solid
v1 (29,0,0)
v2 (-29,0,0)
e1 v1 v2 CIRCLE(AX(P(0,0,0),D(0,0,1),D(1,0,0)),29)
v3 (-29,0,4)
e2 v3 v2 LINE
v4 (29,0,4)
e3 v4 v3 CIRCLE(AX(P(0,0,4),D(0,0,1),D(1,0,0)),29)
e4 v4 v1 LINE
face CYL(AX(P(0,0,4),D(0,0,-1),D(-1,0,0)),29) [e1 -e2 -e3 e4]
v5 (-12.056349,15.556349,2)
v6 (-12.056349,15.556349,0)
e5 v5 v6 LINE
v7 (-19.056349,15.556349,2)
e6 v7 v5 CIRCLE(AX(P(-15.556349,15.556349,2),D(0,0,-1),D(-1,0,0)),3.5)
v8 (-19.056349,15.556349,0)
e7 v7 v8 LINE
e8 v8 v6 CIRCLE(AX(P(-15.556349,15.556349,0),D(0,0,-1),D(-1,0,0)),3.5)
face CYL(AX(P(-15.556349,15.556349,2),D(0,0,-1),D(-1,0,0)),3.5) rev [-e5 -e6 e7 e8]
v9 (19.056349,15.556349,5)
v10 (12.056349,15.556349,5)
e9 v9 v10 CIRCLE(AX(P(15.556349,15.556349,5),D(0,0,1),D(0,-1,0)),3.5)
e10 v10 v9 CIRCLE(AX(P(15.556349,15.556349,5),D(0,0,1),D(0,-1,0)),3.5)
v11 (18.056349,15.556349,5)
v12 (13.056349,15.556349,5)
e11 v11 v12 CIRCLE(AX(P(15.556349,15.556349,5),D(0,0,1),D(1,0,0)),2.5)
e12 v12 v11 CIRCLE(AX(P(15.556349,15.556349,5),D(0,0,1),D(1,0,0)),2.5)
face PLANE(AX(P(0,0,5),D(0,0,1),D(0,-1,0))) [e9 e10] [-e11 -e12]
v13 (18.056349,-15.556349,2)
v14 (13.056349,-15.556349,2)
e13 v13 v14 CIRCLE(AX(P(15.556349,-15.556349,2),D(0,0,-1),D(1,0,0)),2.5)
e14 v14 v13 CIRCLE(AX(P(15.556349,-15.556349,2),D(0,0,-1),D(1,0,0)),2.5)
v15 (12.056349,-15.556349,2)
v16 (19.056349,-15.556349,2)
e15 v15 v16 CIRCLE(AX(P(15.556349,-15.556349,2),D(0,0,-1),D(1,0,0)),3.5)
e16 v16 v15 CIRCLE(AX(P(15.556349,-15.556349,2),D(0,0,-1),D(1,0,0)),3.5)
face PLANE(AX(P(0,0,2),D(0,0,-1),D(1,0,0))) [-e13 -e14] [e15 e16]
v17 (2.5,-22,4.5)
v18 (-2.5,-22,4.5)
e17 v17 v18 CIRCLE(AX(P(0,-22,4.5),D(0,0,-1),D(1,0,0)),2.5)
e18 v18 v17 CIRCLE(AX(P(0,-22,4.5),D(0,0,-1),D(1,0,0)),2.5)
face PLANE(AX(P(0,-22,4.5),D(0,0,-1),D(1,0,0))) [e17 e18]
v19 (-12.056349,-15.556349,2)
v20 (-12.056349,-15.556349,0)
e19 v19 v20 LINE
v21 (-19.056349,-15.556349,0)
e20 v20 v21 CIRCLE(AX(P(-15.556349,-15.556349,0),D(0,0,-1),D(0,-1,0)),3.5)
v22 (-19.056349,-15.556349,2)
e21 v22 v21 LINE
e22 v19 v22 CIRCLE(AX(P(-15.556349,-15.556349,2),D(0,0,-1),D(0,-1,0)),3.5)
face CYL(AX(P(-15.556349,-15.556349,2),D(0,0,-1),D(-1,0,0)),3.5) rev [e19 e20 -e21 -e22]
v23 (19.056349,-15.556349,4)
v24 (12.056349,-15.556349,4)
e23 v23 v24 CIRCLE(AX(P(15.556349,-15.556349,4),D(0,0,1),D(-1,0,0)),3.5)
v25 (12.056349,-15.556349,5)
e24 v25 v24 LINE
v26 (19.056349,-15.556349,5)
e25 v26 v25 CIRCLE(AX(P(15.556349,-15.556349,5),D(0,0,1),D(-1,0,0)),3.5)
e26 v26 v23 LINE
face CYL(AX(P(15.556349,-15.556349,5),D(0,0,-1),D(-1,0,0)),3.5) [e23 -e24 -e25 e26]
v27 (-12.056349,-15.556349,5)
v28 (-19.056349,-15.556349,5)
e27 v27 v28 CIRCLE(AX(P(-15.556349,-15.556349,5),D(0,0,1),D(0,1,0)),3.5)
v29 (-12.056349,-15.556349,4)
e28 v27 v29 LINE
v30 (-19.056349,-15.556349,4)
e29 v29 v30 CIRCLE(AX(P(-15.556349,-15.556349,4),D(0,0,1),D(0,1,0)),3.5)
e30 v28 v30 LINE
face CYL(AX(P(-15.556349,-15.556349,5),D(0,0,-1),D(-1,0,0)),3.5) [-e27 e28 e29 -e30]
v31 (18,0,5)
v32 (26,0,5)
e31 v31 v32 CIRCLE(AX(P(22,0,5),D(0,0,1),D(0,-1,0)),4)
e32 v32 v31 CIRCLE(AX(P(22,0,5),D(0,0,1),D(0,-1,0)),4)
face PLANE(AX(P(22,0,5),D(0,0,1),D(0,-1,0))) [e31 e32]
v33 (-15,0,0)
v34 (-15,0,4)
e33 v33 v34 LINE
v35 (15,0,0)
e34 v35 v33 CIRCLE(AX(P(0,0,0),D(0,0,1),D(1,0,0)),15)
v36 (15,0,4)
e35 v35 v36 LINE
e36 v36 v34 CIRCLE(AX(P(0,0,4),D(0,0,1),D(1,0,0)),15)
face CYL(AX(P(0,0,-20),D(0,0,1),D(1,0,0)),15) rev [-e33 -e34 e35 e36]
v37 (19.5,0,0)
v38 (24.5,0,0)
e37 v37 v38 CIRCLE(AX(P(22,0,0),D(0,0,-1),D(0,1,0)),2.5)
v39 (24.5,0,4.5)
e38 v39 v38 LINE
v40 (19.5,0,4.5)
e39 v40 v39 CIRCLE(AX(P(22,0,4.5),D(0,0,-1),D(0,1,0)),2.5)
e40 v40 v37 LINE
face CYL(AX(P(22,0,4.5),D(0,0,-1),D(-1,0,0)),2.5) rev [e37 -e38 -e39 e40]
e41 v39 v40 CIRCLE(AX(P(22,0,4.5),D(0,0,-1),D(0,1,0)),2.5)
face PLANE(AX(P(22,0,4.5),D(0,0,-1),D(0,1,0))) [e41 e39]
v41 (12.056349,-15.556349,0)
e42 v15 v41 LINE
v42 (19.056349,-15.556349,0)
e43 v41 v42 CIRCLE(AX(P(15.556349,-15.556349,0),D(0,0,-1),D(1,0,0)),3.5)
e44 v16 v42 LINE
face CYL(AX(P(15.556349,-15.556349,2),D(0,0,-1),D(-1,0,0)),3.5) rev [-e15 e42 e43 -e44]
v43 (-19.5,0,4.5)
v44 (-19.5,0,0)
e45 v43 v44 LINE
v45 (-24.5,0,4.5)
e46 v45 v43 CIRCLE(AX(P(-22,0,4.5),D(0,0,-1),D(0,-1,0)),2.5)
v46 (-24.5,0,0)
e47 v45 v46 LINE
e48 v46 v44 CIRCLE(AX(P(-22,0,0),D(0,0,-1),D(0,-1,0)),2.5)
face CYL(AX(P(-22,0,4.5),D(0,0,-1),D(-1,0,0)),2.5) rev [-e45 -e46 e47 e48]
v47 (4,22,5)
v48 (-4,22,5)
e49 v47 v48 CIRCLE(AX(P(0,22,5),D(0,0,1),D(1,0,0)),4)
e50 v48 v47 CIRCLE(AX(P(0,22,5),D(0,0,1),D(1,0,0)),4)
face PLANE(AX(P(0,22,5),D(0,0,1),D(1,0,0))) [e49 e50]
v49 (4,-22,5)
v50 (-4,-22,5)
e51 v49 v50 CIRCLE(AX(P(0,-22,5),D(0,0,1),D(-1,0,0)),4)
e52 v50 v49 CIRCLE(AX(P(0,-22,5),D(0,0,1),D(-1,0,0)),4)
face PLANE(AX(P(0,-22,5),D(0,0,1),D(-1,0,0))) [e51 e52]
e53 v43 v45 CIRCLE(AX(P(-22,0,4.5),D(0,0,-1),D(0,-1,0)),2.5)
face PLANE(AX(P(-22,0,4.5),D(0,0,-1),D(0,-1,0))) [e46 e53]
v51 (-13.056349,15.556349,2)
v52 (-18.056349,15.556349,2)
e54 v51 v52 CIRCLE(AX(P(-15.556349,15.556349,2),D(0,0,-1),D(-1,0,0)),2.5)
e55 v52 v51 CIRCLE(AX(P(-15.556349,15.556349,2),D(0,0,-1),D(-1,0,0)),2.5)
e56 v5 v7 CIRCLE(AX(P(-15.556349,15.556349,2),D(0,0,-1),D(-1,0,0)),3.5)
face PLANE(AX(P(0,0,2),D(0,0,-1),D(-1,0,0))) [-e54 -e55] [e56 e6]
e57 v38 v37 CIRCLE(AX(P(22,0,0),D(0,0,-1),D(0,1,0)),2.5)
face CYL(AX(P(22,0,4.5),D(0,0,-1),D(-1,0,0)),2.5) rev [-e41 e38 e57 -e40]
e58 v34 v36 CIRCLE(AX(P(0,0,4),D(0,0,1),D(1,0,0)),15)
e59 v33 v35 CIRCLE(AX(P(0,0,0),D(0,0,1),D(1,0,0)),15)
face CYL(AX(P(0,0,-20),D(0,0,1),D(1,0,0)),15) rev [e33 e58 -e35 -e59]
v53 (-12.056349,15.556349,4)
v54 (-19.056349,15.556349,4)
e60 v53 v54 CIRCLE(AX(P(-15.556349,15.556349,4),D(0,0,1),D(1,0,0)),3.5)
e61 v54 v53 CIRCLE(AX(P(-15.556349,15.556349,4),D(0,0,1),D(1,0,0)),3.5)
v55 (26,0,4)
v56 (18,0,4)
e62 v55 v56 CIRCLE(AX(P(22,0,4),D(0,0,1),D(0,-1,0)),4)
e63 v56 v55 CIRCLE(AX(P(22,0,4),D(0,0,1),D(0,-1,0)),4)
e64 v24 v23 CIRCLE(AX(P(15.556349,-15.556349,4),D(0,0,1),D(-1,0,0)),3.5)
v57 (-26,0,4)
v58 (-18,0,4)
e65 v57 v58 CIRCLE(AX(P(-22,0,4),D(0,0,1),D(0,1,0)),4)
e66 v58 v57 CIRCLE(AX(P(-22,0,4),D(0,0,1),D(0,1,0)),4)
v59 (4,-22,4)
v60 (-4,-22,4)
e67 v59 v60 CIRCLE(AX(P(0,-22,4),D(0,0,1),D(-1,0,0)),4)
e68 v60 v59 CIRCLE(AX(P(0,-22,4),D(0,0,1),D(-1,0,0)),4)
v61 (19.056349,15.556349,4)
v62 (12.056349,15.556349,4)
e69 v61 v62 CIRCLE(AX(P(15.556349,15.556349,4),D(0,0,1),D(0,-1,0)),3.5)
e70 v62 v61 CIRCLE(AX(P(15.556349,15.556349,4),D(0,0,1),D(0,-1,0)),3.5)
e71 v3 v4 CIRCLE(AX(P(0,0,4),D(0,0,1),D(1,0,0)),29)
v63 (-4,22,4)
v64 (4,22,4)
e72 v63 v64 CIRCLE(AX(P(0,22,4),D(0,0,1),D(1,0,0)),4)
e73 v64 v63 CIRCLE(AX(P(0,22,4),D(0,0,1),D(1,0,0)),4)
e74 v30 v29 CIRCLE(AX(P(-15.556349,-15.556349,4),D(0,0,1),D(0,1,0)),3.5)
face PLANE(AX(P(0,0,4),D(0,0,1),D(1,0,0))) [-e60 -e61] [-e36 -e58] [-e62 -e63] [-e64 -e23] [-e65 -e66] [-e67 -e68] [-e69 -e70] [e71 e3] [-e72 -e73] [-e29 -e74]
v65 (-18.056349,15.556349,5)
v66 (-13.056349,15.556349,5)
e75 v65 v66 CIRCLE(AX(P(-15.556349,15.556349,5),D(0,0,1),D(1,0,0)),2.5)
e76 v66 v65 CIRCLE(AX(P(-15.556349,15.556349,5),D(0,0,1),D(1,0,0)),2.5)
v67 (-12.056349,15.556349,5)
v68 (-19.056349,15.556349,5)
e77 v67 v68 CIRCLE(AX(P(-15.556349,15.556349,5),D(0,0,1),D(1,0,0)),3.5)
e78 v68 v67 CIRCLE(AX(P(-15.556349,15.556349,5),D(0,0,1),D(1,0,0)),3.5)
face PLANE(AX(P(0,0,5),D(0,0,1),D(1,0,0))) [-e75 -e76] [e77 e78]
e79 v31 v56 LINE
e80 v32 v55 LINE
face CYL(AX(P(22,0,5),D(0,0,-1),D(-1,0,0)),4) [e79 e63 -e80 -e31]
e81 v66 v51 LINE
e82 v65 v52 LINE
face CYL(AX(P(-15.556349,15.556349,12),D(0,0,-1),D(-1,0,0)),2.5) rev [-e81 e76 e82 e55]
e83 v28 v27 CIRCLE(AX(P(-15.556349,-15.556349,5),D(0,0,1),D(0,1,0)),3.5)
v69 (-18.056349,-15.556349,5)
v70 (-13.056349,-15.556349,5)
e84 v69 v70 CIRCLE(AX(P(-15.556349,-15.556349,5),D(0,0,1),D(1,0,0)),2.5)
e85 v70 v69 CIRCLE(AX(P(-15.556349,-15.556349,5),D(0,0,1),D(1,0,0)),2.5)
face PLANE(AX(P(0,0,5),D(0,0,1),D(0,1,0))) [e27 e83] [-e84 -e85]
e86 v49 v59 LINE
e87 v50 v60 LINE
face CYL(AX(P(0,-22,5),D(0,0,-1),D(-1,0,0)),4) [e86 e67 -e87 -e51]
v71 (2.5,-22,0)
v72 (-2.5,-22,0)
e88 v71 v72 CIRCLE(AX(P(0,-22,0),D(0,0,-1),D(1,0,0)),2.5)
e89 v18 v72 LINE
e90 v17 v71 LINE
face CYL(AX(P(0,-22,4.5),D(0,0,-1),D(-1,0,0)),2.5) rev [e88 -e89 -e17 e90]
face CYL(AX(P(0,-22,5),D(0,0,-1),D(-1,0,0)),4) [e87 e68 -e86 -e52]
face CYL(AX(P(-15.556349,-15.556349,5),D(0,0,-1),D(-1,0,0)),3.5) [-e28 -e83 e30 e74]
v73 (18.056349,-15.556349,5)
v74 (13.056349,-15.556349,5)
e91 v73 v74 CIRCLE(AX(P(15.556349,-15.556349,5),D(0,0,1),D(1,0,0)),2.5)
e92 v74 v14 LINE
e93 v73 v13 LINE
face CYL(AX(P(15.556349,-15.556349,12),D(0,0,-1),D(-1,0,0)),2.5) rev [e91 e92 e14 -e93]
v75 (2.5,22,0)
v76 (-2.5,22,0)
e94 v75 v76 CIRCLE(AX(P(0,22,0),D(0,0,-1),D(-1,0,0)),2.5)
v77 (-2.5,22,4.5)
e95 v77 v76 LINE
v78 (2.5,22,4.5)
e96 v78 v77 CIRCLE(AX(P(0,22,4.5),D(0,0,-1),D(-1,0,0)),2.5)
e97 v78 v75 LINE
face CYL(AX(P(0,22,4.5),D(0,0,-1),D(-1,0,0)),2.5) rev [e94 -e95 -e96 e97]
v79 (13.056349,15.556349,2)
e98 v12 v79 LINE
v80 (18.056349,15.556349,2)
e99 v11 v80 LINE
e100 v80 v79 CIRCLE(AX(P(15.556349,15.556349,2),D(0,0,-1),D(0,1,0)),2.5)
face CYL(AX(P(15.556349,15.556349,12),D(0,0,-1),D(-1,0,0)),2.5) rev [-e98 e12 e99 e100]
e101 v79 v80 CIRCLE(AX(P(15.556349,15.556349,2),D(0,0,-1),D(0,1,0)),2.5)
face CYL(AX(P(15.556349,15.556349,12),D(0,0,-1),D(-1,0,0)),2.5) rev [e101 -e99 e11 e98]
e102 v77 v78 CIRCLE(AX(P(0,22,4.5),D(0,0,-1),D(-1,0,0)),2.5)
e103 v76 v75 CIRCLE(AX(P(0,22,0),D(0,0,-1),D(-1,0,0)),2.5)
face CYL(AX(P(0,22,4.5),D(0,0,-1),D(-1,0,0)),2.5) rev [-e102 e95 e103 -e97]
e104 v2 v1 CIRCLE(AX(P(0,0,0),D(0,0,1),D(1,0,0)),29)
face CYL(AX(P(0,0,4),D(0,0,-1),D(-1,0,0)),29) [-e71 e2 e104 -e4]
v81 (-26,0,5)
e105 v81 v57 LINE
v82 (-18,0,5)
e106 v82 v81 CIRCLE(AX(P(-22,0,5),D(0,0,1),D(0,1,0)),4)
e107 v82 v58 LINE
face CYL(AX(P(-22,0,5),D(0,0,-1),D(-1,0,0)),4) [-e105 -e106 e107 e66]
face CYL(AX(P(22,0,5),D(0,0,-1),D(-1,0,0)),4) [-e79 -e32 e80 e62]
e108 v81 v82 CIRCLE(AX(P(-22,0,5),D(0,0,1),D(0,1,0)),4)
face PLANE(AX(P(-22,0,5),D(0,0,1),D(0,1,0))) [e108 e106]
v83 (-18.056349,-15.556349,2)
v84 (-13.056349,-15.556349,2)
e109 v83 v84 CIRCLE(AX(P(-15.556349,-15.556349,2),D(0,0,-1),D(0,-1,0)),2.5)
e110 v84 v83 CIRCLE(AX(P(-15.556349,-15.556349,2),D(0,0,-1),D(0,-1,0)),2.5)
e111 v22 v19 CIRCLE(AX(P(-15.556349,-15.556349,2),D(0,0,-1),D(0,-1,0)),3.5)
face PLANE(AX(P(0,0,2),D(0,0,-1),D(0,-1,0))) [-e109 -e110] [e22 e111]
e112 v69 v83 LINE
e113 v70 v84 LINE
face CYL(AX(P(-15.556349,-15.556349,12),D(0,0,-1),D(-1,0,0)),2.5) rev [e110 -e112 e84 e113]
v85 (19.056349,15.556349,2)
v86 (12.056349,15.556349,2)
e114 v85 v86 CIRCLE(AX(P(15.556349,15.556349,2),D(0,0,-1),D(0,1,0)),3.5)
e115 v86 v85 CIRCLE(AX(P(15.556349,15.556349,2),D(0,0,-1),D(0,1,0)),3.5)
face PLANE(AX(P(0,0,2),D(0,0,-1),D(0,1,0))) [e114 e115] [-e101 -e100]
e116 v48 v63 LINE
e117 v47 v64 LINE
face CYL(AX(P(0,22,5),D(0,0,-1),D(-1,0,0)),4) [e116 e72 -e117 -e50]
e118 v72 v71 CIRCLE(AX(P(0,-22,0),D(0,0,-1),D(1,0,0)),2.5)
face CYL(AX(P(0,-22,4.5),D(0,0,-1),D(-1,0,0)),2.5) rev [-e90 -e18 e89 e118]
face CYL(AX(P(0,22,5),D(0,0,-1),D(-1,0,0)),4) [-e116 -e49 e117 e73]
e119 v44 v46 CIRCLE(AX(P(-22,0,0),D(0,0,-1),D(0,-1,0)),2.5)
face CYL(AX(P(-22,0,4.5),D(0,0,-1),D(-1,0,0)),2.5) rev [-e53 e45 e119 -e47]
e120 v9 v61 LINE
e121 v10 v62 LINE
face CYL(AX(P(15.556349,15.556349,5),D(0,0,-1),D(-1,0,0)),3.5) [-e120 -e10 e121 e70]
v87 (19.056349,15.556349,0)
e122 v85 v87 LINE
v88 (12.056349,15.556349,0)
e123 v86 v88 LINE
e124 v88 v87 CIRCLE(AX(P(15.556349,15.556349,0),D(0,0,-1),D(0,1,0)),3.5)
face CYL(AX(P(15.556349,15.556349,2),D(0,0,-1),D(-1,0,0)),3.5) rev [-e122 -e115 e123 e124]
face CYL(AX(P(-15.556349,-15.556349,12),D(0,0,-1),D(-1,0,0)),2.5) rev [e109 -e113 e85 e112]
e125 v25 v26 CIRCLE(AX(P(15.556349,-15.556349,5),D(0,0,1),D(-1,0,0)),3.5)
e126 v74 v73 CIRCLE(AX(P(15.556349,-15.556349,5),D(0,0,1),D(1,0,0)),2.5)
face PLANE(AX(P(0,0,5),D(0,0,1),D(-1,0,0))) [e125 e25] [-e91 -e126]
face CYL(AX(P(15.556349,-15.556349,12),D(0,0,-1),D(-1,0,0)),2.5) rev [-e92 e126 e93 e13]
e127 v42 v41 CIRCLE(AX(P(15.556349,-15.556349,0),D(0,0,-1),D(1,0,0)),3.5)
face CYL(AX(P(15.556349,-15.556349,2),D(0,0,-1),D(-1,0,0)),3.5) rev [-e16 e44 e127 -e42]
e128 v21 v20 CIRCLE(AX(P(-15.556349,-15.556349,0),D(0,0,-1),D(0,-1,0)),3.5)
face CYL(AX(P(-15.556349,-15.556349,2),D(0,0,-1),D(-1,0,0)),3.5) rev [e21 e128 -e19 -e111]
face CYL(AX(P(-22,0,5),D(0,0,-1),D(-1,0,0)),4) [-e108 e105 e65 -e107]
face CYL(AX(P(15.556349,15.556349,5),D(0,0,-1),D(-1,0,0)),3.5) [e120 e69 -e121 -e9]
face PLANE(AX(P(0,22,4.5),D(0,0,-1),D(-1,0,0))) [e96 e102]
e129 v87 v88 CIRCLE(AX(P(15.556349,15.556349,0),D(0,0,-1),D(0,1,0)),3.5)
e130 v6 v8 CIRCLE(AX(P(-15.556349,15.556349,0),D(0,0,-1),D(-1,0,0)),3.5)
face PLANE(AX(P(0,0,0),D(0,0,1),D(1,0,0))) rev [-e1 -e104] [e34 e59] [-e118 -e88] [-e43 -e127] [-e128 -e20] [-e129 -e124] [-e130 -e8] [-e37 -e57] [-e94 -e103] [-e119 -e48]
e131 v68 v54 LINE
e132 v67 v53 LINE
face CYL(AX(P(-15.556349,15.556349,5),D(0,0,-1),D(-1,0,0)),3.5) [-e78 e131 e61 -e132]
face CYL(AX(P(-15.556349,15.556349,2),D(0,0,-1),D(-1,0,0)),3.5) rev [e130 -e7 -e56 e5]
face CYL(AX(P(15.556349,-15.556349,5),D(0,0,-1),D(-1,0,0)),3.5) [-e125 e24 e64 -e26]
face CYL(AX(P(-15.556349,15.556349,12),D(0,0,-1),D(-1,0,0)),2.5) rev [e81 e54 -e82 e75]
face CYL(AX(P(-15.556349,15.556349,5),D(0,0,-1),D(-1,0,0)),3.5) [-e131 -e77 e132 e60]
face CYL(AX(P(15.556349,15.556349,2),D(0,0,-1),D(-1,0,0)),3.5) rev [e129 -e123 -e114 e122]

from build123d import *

# Parameters (mm, degrees)
SKETCH1_R           = 29
BOSS_EXTRUDE1_DEPTH = 4
SKETCH2_R           = 15
CUT_EXTRUDE1_DEPTH  = 24
SKETCH3_R           = 4
BOSS_EXTRUDE2_DEPTH = 1
SKETCH5_R           = 2.5
CUT_EXTRUDE2_DEPTH  = 4.5
CIRPATTERN1_COUNT   = 4
SKETCH6_R           = 3.5
BOSS_EXTRUDE3_DEPTH = 1
SKETCH7_R           = 3.5
CUT_EXTRUDE3_DEPTH  = 2
SKETCH8_R           = 2.5
CUT_EXTRUDE4_DEPTH  = 10
CIRPATTERN2_COUNT   = 4


with BuildPart() as part:
    # Sketch1 → Boss-Extrude1 (new body)
    with BuildSketch(Plane.XY):
        Circle(SKETCH1_R)
    extrude(amount=BOSS_EXTRUDE1_DEPTH)

    # Sketch2 → Cut-Extrude1 (cut)
    with BuildSketch(Plane.XY.offset(4)):
        Circle(SKETCH2_R)
    extrude(amount=-CUT_EXTRUDE1_DEPTH, mode=Mode.SUBTRACT)

    # Sketch3 → Boss-Extrude2 (add)
    with BuildSketch(Plane.XY.offset(4)):
        with Locations((0, 22)):
            Circle(SKETCH3_R)
    boss_extrude2 = extrude(amount=BOSS_EXTRUDE2_DEPTH)

    # Sketch5 → Cut-Extrude2 (cut)
    with BuildSketch(Plane(origin=(0, 0, 0), x_dir=(-1, 0, 0), z_dir=(0, 0, -1))):
        with Locations((0, 22)):
            Circle(SKETCH5_R)
    cut_extrude2 = extrude(amount=-CUT_EXTRUDE2_DEPTH, mode=Mode.SUBTRACT)

    # CirPattern1: Boss-Extrude2, Cut-Extrude2 ×4 about axis
    cirpattern1_axis = Axis((0, 0, 0), (0, 0, 1))
    add([boss_extrude2.rotate(cirpattern1_axis, i * 360 / CIRPATTERN1_COUNT) for i in range(1, CIRPATTERN1_COUNT)])
    add([cut_extrude2.rotate(cirpattern1_axis, i * 360 / CIRPATTERN1_COUNT) for i in range(1, CIRPATTERN1_COUNT)], mode=Mode.SUBTRACT)

    # Sketch6 → Boss-Extrude3 (add)
    with BuildSketch(Plane.XY.offset(4)):
        with Locations((-15.556349186, 15.556349186)):
            Circle(SKETCH6_R)
    boss_extrude3 = extrude(amount=BOSS_EXTRUDE3_DEPTH)

    # Sketch7 → Cut-Extrude3 (cut)
    with BuildSketch(Plane(origin=(0, 0, 0), x_dir=(-1, 0, 0), z_dir=(0, 0, -1))):
        with Locations(Location((15.556349186, 15.556349186, 0), (0, 0, 180))):
            Circle(SKETCH7_R)
    cut_extrude3 = extrude(amount=-CUT_EXTRUDE3_DEPTH, mode=Mode.SUBTRACT)

    # Sketch8 → Cut-Extrude4 (cut)
    with BuildSketch(Plane(origin=(0, 0, 2), x_dir=(-1, 0, 0), z_dir=(0, 0, -1))):
        with Locations((15.556349186, 15.556349186)):
            Circle(SKETCH8_R)
    cut_extrude4 = extrude(amount=-CUT_EXTRUDE4_DEPTH, mode=Mode.SUBTRACT)

    # CirPattern2: Boss-Extrude3, Cut-Extrude3, Cut-Extrude4 ×4 about axis
    cirpattern2_axis = Axis((0, 0, 0), (0, 0, 1))
    add([boss_extrude3.rotate(cirpattern2_axis, i * 360 / CIRPATTERN2_COUNT) for i in range(1, CIRPATTERN2_COUNT)])
    add([cut_extrude3.rotate(cirpattern2_axis, i * 360 / CIRPATTERN2_COUNT) for i in range(1, CIRPATTERN2_COUNT)], mode=Mode.SUBTRACT)
    add([cut_extrude4.rotate(cirpattern2_axis, i * 360 / CIRPATTERN2_COUNT) for i in range(1, CIRPATTERN2_COUNT)], mode=Mode.SUBTRACT)


solid = part.part
